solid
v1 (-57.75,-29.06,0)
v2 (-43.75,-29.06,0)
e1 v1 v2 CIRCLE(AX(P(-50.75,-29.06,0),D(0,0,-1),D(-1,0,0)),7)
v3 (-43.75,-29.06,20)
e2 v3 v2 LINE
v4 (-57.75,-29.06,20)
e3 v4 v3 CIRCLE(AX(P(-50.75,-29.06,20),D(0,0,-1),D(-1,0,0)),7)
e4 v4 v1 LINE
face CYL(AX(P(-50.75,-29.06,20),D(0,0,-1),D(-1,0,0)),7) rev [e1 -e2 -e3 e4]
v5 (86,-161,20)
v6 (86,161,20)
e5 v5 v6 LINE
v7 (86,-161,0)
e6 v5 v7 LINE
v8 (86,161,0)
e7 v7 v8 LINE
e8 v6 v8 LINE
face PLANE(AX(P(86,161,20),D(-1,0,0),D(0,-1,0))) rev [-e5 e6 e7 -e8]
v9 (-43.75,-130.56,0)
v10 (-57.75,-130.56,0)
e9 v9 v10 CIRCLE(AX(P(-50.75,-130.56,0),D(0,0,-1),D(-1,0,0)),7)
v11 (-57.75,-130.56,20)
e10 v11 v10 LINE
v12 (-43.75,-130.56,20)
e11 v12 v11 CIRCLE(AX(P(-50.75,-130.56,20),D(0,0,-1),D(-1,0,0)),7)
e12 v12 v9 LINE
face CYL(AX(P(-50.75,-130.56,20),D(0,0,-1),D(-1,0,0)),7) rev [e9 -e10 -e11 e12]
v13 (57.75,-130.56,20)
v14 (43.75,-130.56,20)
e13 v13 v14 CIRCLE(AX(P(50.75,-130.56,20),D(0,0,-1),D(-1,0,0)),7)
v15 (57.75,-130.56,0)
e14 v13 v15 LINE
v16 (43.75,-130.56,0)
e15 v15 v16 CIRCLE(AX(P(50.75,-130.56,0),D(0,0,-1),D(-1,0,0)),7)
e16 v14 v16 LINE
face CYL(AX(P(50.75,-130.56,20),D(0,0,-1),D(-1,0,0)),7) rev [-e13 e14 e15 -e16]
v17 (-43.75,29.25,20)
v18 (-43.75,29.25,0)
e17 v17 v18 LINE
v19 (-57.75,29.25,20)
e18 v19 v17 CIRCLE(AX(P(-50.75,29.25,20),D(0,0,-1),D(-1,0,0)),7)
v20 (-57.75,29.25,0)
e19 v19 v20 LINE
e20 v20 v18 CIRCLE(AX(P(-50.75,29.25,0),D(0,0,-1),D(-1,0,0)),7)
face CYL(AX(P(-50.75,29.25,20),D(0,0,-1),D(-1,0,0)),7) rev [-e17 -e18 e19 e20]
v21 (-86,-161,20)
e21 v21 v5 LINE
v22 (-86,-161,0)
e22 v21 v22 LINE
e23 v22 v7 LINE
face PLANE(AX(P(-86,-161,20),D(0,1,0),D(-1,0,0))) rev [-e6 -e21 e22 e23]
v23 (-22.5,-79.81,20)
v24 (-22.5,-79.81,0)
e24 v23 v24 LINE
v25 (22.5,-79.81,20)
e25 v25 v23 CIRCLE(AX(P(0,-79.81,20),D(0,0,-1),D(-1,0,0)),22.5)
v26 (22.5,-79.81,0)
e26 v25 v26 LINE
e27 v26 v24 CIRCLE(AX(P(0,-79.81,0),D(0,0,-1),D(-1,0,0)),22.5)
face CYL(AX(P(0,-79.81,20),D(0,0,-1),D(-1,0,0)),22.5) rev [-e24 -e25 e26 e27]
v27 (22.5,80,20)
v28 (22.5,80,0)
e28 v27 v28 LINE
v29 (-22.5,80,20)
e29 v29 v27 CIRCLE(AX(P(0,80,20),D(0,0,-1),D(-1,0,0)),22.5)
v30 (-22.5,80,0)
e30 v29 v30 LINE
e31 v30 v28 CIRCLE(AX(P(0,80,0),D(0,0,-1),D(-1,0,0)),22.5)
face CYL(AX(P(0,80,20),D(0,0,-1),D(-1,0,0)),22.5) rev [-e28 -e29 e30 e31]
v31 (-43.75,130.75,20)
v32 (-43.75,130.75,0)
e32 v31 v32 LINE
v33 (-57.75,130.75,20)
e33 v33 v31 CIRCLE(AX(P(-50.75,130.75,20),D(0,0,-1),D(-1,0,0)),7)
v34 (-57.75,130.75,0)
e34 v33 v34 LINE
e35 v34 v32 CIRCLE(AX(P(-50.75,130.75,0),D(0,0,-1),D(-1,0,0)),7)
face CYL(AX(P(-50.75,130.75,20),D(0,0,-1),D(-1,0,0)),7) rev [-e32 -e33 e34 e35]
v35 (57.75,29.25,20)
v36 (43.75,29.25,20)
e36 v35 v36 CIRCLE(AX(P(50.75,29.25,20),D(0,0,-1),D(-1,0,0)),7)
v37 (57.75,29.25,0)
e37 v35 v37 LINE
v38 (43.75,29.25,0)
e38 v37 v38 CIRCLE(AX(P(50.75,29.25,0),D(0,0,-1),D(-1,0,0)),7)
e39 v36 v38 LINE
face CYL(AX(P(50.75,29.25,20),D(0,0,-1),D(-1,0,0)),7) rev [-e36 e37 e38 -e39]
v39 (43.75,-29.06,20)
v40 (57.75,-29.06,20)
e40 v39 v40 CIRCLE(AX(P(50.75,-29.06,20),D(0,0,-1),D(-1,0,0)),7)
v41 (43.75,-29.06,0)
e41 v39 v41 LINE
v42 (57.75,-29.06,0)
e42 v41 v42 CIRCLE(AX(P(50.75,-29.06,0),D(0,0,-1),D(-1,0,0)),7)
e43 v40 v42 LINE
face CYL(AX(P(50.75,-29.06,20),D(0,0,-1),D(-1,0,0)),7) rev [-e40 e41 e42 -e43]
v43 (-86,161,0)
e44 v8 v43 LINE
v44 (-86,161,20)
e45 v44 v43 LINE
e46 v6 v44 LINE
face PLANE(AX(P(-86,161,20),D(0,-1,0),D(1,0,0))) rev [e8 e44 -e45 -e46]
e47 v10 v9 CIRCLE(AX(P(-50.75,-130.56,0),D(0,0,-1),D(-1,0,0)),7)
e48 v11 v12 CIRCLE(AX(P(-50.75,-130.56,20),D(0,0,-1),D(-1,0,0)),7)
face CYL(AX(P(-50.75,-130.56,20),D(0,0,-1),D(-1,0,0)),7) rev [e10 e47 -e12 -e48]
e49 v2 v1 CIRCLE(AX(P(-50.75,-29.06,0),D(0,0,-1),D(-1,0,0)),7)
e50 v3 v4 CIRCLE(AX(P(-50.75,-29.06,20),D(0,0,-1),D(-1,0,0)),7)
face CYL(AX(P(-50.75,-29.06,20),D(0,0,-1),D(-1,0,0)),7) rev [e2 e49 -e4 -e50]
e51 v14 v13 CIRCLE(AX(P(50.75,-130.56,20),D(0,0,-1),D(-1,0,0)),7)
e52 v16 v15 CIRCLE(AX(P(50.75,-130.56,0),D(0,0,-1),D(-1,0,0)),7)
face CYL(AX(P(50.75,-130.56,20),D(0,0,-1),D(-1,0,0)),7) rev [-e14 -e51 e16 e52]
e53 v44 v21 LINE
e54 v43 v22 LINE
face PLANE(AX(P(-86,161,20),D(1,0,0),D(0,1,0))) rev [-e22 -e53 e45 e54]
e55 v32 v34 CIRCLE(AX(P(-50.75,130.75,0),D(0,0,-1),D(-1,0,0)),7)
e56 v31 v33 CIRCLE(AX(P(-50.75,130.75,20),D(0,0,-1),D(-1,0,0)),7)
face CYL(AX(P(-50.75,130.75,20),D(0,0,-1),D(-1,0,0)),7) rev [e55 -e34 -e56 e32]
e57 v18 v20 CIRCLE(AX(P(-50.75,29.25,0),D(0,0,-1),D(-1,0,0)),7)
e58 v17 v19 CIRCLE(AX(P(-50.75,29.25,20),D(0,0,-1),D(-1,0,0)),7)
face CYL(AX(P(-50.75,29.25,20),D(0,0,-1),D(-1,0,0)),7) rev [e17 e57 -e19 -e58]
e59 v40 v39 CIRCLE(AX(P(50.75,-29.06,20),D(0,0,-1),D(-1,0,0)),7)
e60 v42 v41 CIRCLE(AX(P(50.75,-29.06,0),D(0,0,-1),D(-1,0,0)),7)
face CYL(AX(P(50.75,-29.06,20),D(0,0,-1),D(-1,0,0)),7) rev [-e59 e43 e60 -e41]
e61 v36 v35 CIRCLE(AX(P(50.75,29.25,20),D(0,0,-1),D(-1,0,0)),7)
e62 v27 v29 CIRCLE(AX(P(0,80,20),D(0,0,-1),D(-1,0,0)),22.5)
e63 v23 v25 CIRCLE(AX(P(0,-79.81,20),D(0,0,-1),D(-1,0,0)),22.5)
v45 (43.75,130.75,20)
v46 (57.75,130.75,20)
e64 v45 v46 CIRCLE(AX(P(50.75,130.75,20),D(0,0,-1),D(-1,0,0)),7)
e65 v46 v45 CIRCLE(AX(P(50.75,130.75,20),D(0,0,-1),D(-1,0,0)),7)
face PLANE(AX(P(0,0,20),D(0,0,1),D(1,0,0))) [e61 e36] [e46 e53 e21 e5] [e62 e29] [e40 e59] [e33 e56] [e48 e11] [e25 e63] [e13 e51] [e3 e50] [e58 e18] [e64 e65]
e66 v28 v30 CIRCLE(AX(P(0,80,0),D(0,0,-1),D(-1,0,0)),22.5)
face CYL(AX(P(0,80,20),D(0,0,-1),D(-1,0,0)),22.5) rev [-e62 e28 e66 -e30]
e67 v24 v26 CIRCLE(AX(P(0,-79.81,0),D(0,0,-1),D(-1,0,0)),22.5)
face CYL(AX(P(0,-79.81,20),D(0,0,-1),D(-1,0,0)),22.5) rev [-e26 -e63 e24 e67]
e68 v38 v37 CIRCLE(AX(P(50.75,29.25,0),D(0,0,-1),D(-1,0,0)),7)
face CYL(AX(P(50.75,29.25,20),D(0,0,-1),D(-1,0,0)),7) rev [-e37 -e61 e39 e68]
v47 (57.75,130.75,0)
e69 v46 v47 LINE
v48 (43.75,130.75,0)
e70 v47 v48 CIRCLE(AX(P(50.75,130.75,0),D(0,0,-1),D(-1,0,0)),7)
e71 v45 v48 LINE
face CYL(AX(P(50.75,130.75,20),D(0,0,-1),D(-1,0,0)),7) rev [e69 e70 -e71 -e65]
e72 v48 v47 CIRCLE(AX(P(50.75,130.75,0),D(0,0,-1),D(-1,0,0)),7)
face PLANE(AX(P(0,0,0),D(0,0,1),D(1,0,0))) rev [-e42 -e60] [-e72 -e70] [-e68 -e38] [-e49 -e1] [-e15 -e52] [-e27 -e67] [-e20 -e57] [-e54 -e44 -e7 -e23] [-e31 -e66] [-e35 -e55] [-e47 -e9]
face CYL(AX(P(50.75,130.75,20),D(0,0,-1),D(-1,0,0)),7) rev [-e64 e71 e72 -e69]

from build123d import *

# Parameters (mm, degrees)
SKETCH_1_W          = 172
SKETCH_1_H          = 322
EXTRUDE_1_DEPTH     = 20
SKETCH_3_R          = 22.5
SKETCH_3_R_2        = 7
CUT_EXTRUDE_1_DEPTH = 184.621894119


with BuildPart() as part:
    # 草图1 → 凸台-拉伸1 (new body)
    with BuildSketch(Plane.XY):
        Rectangle(SKETCH_1_W, SKETCH_1_H)
    extrude(amount=EXTRUDE_1_DEPTH)

    # 草图3 → 切除-拉伸1 (cut, through all)
    with BuildSketch(Plane(origin=(0, 0, 0), x_dir=(-1, 0, 0), z_dir=(0, 0, -1))):
        with Locations((0, 80)):
            Circle(SKETCH_3_R)
        with Locations((-50.75, 130.75)):
            Circle(SKETCH_3_R_2)
        with Locations((50.75, 130.75)):
            Circle(SKETCH_3_R_2)
        with Locations((-50.75, 29.25)):
            Circle(SKETCH_3_R_2)
        with Locations((50.75, 29.25)):
            Circle(SKETCH_3_R_2)
        with Locations((0, -79.81)):
            Circle(SKETCH_3_R)
        with Locations((-50.75, -29.06)):
            Circle(SKETCH_3_R_2)
        with Locations((50.75, -29.06)):
            Circle(SKETCH_3_R_2)
        with Locations((50.75, -130.56)):
            Circle(SKETCH_3_R_2)
        with Locations((-50.75, -130.56)):
            Circle(SKETCH_3_R_2)
    extrude(amount=-CUT_EXTRUDE_1_DEPTH, mode=Mode.SUBTRACT)


solid = part.part
